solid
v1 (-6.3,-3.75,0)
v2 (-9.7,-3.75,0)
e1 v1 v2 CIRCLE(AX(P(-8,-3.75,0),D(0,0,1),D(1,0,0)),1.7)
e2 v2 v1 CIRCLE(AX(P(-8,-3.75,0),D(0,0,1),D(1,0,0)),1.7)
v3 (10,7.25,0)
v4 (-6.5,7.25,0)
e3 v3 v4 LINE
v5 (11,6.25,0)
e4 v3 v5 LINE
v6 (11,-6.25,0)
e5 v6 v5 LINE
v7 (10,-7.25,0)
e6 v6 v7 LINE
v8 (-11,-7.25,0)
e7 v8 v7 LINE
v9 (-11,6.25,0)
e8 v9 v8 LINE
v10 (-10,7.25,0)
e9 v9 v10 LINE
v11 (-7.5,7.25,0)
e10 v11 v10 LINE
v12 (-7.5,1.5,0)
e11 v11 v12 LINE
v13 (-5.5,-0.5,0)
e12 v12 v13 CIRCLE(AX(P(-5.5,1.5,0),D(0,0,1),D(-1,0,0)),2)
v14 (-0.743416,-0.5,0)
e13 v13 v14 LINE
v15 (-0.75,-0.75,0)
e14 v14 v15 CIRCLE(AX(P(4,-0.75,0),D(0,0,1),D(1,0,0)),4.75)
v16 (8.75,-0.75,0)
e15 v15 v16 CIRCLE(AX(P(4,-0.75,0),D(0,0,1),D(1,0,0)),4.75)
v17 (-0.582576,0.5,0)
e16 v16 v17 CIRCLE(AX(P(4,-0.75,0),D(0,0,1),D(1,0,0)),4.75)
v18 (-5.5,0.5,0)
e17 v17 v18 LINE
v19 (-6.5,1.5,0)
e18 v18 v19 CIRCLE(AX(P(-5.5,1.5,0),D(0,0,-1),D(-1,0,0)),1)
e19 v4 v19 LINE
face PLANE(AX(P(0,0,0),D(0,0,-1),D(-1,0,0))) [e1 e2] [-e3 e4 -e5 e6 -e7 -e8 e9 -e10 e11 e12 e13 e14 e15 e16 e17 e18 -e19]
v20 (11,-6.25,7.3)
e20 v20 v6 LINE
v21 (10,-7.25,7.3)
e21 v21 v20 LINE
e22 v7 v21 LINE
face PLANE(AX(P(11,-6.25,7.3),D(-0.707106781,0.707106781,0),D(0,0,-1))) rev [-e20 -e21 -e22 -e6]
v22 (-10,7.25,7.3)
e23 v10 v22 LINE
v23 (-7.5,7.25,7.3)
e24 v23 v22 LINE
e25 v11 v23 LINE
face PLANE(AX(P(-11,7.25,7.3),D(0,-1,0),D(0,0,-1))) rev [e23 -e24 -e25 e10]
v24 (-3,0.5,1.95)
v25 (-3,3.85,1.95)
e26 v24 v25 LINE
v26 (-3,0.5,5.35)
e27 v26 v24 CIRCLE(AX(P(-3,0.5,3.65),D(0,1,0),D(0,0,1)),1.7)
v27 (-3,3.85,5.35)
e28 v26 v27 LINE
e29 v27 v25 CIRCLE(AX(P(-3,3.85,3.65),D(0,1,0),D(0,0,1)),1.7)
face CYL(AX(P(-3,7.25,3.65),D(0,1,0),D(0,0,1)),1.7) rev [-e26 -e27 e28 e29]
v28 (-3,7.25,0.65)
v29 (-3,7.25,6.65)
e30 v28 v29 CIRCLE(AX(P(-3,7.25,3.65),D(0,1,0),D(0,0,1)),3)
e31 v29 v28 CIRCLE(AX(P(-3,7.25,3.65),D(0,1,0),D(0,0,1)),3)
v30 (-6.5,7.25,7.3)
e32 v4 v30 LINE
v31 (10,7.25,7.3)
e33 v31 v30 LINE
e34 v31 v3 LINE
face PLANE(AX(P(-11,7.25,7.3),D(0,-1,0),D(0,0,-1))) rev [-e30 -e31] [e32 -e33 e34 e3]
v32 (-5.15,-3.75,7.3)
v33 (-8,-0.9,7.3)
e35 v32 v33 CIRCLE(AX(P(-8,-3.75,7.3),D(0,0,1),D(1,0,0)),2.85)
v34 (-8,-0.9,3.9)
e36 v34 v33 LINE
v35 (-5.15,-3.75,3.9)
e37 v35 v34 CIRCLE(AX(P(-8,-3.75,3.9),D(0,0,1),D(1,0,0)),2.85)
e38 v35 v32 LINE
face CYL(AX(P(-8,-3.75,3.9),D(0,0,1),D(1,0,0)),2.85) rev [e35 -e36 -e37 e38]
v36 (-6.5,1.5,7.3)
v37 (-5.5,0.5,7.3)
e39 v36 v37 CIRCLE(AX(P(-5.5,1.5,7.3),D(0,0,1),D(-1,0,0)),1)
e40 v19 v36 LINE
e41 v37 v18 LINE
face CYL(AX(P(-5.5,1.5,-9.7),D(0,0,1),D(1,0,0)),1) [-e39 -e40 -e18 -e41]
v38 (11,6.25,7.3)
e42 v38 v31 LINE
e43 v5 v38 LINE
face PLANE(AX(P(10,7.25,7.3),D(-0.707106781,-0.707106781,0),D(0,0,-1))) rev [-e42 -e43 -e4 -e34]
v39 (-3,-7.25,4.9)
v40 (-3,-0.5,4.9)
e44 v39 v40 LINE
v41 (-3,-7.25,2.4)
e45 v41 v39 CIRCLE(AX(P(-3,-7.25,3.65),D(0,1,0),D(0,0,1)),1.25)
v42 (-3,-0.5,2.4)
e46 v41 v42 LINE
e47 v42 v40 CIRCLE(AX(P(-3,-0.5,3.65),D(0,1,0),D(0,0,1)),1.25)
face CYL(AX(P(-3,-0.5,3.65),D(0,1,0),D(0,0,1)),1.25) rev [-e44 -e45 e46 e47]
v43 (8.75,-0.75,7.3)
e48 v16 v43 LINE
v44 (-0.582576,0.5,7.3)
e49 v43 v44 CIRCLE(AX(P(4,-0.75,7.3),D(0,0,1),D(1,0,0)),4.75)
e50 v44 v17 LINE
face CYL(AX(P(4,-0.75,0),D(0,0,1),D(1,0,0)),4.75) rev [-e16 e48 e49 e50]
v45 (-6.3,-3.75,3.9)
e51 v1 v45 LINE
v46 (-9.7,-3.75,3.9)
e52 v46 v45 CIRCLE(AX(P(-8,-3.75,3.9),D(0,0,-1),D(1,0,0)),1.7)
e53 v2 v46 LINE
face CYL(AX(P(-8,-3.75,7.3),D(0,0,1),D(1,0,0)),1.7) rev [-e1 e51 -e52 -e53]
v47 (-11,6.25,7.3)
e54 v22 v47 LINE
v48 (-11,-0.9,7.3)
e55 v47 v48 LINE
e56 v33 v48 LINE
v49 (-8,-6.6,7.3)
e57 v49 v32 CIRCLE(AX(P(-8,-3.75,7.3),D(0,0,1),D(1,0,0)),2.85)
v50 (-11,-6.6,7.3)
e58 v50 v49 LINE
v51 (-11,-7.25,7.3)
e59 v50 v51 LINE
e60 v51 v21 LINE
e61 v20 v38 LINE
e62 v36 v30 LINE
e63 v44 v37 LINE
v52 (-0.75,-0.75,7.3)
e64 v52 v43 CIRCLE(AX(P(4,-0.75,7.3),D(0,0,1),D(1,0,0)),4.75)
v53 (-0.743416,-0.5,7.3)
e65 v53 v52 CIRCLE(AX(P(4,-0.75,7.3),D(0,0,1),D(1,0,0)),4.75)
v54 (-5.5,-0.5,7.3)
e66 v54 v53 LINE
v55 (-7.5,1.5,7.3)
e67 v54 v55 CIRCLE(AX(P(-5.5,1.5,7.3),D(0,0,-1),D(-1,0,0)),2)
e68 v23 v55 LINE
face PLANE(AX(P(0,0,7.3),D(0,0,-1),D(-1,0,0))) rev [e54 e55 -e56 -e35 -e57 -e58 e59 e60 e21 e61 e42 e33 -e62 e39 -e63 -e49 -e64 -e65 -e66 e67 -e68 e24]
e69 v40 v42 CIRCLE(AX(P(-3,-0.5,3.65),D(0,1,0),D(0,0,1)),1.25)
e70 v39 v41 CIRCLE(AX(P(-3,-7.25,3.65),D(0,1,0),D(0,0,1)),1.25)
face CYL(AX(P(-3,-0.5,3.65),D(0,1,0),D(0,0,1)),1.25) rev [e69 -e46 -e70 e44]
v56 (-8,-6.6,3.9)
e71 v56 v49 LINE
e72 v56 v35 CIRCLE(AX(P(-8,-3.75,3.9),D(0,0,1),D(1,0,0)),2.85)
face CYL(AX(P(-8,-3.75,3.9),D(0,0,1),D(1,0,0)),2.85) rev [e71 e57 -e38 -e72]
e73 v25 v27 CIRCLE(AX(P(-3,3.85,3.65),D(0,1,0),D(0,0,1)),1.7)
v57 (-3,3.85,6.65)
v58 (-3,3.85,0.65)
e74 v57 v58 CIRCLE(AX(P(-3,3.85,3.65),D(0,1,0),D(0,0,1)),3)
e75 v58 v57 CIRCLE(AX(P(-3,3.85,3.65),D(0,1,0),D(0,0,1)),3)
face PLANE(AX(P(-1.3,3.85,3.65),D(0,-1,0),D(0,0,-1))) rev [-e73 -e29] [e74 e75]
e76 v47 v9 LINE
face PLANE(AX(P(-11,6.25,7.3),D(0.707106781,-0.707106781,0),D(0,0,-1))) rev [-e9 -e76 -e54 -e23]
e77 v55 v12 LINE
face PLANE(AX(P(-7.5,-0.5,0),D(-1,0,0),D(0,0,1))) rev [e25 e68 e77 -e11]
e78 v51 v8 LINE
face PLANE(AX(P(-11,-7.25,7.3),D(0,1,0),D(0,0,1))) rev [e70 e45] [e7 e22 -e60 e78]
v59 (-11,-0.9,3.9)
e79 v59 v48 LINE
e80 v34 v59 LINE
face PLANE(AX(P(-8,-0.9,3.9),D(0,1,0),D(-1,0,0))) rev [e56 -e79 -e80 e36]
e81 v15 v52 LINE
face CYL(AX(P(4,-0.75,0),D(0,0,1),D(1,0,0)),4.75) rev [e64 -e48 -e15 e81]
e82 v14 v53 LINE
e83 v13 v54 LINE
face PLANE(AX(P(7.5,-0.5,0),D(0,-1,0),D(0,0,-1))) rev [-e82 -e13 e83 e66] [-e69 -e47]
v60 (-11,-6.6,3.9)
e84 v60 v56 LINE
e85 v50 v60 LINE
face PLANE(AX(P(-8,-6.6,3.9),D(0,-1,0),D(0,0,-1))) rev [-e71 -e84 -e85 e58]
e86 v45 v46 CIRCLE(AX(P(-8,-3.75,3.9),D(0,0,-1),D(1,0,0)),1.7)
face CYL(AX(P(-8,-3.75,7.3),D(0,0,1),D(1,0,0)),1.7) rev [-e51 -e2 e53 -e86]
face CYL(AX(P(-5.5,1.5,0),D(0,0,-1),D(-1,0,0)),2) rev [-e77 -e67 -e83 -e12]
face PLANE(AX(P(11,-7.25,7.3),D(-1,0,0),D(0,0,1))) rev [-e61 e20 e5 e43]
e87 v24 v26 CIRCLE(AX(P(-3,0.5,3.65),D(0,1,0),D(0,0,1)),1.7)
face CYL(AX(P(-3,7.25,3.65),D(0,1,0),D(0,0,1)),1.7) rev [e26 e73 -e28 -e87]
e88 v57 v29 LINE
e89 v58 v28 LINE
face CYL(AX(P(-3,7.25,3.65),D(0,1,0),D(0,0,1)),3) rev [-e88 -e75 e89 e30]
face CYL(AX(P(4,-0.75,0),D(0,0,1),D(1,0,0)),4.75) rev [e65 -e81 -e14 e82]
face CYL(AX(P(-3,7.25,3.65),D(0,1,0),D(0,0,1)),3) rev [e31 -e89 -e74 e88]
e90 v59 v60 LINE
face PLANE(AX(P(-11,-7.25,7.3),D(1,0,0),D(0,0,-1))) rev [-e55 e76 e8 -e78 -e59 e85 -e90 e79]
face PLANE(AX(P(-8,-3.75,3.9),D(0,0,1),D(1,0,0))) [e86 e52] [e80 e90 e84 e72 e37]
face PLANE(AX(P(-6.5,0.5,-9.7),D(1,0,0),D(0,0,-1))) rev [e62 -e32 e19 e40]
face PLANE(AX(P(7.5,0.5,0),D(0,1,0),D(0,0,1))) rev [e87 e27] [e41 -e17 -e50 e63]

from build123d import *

# Parameters (mm, degrees)
SKETCH1_W                                            = 22
SKETCH1_H                                            = 14.5
BOSS_EXTRUDE1_DEPTH                                  = 7.3
SKETCH2_R                                            = 4.75
CUT_EXTRUDE1_DEPTH                                   = 16.061623418
F_3_4_3_4_DIAMETER_HOLE1_D                           = 3.4
SKETCH5_W                                            = 15
SKETCH5_H                                            = 1
CUT_EXTRUDE2_DEPTH                                   = 16.061623418
SKETCH6_W                                            = 1
SKETCH6_H                                            = 6.75
CUT_EXTRUDE3_DEPTH                                   = 17
FILLET1_R                                            = 2
FILLET2_R                                            = 1
SKETCH7_W                                            = 1.25
SKETCH7_H                                            = 6.75
HOLE_SIZE_PER_SOCKET_HEAD_CAP_SCREW_TYPE_D           = 3.4
HOLE_SIZE_PER_SOCKET_HEAD_CAP_SCREW_TYPE_DEPTH       = 7.749
HOLE_SIZE_PER_SOCKET_HEAD_CAP_SCREW_TYPE_CBORE_D     = 6
HOLE_SIZE_PER_SOCKET_HEAD_CAP_SCREW_TYPE_CBORE_DEPTH = 3.4
CUT_EXTRUDE4_DEPTH                                   = 3.4
CHAMFER1_SIZE                                        = 1


with BuildPart() as part:
    # Sketch1 → Boss-Extrude1 (new body)
    with BuildSketch(Plane.XY):
        Rectangle(SKETCH1_W, SKETCH1_H)
    extrude(amount=BOSS_EXTRUDE1_DEPTH)

    # Sketch2 → Cut-Extrude1 (cut, through all)
    with BuildSketch(Plane.XY.offset(7.3)):
        with Locations((4, -0.75)):
            Circle(SKETCH2_R)
    extrude(amount=-CUT_EXTRUDE1_DEPTH, mode=Mode.SUBTRACT)

    # Ø3.4 (3.4) Diameter Hole1 (through all)
    with Locations(Plane.XY.offset(7.3)):
        with Locations((-8, -3.75)):
            Hole(F_3_4_3_4_DIAMETER_HOLE1_D / 2)

    # Sketch5 → Cut-Extrude2 (cut, through all)
    with BuildSketch(Plane.XY.offset(7.3)):
        Rectangle(SKETCH5_W, SKETCH5_H)
    extrude(amount=-CUT_EXTRUDE2_DEPTH, mode=Mode.SUBTRACT)

    # Sketch6 → Cut-Extrude3 (cut)
    with BuildSketch(Plane.XY.offset(7.3)):
        with Locations((-7, 3.875)):
            Rectangle(SKETCH6_W, SKETCH6_H)
    extrude(amount=-CUT_EXTRUDE3_DEPTH, mode=Mode.SUBTRACT)

    # Fillet1
    fillet1_edges = [part.edges().sort_by_distance(p)[0] for p in [
        (-7.5, -0.5, 3.65),
    ]]
    fillet(fillet1_edges, radius=FILLET1_R)

    # Fillet2
    fillet2_edges = [part.edges().sort_by_distance(p)[0] for p in [
        (-6.5, 0.5, 3.65),
    ]]
    fillet(fillet2_edges, radius=FILLET2_R)

    # Sketch7 → M3 Tapped Hole1 (revolve, cut)
    with BuildSketch(Plane(origin=(-3, -0.5, 3.65), x_dir=(0, 0, 1), z_dir=(1, 0, 0))):
        with Locations((0.625, 3.375)):
            Rectangle(SKETCH7_W, SKETCH7_H)
    revolve(axis=Axis((-3, 5.85, 3.65), (0, -1, 0)), mode=Mode.SUBTRACT)

    # Hole size per socket head cap screw type 3
    with Locations(Plane(origin=(0, 7.25, 0), x_dir=(1, 0, 0), z_dir=(0, 1, 0))):
        with Locations((-3, -3.65)):
            CounterBoreHole(HOLE_SIZE_PER_SOCKET_HEAD_CAP_SCREW_TYPE_D / 2, HOLE_SIZE_PER_SOCKET_HEAD_CAP_SCREW_TYPE_CBORE_D / 2, HOLE_SIZE_PER_SOCKET_HEAD_CAP_SCREW_TYPE_CBORE_DEPTH, depth=HOLE_SIZE_PER_SOCKET_HEAD_CAP_SCREW_TYPE_DEPTH)

    # Sketch13 → Cut-Extrude4 (cut)
    with BuildSketch(Plane.XY.offset(7.3)):
        with BuildLine():
            Line((-8, -6.6), (-13.475777531, -6.6))
            ThreePointArc((-13.475777531, -6.6), (-16.325777531, -3.75), (-13.475777531, -0.9))
            Line((-13.475777531, -0.9), (-8, -0.9))
            ThreePointArc((-8, -0.9), (-5.15, -3.75), (-8, -6.6))
        make_face()
    extrude(amount=-CUT_EXTRUDE4_DEPTH, mode=Mode.SUBTRACT)

    # Chamfer1
    chamfer1_edges = [part.edges().sort_by_distance(p)[0] for p in [
        (11, -7.25, 3.65),
        (-11, 7.25, 3.65),
        (11, 7.25, 3.65),
    ]]
    chamfer(chamfer1_edges, length=CHAMFER1_SIZE)


solid = part.part
